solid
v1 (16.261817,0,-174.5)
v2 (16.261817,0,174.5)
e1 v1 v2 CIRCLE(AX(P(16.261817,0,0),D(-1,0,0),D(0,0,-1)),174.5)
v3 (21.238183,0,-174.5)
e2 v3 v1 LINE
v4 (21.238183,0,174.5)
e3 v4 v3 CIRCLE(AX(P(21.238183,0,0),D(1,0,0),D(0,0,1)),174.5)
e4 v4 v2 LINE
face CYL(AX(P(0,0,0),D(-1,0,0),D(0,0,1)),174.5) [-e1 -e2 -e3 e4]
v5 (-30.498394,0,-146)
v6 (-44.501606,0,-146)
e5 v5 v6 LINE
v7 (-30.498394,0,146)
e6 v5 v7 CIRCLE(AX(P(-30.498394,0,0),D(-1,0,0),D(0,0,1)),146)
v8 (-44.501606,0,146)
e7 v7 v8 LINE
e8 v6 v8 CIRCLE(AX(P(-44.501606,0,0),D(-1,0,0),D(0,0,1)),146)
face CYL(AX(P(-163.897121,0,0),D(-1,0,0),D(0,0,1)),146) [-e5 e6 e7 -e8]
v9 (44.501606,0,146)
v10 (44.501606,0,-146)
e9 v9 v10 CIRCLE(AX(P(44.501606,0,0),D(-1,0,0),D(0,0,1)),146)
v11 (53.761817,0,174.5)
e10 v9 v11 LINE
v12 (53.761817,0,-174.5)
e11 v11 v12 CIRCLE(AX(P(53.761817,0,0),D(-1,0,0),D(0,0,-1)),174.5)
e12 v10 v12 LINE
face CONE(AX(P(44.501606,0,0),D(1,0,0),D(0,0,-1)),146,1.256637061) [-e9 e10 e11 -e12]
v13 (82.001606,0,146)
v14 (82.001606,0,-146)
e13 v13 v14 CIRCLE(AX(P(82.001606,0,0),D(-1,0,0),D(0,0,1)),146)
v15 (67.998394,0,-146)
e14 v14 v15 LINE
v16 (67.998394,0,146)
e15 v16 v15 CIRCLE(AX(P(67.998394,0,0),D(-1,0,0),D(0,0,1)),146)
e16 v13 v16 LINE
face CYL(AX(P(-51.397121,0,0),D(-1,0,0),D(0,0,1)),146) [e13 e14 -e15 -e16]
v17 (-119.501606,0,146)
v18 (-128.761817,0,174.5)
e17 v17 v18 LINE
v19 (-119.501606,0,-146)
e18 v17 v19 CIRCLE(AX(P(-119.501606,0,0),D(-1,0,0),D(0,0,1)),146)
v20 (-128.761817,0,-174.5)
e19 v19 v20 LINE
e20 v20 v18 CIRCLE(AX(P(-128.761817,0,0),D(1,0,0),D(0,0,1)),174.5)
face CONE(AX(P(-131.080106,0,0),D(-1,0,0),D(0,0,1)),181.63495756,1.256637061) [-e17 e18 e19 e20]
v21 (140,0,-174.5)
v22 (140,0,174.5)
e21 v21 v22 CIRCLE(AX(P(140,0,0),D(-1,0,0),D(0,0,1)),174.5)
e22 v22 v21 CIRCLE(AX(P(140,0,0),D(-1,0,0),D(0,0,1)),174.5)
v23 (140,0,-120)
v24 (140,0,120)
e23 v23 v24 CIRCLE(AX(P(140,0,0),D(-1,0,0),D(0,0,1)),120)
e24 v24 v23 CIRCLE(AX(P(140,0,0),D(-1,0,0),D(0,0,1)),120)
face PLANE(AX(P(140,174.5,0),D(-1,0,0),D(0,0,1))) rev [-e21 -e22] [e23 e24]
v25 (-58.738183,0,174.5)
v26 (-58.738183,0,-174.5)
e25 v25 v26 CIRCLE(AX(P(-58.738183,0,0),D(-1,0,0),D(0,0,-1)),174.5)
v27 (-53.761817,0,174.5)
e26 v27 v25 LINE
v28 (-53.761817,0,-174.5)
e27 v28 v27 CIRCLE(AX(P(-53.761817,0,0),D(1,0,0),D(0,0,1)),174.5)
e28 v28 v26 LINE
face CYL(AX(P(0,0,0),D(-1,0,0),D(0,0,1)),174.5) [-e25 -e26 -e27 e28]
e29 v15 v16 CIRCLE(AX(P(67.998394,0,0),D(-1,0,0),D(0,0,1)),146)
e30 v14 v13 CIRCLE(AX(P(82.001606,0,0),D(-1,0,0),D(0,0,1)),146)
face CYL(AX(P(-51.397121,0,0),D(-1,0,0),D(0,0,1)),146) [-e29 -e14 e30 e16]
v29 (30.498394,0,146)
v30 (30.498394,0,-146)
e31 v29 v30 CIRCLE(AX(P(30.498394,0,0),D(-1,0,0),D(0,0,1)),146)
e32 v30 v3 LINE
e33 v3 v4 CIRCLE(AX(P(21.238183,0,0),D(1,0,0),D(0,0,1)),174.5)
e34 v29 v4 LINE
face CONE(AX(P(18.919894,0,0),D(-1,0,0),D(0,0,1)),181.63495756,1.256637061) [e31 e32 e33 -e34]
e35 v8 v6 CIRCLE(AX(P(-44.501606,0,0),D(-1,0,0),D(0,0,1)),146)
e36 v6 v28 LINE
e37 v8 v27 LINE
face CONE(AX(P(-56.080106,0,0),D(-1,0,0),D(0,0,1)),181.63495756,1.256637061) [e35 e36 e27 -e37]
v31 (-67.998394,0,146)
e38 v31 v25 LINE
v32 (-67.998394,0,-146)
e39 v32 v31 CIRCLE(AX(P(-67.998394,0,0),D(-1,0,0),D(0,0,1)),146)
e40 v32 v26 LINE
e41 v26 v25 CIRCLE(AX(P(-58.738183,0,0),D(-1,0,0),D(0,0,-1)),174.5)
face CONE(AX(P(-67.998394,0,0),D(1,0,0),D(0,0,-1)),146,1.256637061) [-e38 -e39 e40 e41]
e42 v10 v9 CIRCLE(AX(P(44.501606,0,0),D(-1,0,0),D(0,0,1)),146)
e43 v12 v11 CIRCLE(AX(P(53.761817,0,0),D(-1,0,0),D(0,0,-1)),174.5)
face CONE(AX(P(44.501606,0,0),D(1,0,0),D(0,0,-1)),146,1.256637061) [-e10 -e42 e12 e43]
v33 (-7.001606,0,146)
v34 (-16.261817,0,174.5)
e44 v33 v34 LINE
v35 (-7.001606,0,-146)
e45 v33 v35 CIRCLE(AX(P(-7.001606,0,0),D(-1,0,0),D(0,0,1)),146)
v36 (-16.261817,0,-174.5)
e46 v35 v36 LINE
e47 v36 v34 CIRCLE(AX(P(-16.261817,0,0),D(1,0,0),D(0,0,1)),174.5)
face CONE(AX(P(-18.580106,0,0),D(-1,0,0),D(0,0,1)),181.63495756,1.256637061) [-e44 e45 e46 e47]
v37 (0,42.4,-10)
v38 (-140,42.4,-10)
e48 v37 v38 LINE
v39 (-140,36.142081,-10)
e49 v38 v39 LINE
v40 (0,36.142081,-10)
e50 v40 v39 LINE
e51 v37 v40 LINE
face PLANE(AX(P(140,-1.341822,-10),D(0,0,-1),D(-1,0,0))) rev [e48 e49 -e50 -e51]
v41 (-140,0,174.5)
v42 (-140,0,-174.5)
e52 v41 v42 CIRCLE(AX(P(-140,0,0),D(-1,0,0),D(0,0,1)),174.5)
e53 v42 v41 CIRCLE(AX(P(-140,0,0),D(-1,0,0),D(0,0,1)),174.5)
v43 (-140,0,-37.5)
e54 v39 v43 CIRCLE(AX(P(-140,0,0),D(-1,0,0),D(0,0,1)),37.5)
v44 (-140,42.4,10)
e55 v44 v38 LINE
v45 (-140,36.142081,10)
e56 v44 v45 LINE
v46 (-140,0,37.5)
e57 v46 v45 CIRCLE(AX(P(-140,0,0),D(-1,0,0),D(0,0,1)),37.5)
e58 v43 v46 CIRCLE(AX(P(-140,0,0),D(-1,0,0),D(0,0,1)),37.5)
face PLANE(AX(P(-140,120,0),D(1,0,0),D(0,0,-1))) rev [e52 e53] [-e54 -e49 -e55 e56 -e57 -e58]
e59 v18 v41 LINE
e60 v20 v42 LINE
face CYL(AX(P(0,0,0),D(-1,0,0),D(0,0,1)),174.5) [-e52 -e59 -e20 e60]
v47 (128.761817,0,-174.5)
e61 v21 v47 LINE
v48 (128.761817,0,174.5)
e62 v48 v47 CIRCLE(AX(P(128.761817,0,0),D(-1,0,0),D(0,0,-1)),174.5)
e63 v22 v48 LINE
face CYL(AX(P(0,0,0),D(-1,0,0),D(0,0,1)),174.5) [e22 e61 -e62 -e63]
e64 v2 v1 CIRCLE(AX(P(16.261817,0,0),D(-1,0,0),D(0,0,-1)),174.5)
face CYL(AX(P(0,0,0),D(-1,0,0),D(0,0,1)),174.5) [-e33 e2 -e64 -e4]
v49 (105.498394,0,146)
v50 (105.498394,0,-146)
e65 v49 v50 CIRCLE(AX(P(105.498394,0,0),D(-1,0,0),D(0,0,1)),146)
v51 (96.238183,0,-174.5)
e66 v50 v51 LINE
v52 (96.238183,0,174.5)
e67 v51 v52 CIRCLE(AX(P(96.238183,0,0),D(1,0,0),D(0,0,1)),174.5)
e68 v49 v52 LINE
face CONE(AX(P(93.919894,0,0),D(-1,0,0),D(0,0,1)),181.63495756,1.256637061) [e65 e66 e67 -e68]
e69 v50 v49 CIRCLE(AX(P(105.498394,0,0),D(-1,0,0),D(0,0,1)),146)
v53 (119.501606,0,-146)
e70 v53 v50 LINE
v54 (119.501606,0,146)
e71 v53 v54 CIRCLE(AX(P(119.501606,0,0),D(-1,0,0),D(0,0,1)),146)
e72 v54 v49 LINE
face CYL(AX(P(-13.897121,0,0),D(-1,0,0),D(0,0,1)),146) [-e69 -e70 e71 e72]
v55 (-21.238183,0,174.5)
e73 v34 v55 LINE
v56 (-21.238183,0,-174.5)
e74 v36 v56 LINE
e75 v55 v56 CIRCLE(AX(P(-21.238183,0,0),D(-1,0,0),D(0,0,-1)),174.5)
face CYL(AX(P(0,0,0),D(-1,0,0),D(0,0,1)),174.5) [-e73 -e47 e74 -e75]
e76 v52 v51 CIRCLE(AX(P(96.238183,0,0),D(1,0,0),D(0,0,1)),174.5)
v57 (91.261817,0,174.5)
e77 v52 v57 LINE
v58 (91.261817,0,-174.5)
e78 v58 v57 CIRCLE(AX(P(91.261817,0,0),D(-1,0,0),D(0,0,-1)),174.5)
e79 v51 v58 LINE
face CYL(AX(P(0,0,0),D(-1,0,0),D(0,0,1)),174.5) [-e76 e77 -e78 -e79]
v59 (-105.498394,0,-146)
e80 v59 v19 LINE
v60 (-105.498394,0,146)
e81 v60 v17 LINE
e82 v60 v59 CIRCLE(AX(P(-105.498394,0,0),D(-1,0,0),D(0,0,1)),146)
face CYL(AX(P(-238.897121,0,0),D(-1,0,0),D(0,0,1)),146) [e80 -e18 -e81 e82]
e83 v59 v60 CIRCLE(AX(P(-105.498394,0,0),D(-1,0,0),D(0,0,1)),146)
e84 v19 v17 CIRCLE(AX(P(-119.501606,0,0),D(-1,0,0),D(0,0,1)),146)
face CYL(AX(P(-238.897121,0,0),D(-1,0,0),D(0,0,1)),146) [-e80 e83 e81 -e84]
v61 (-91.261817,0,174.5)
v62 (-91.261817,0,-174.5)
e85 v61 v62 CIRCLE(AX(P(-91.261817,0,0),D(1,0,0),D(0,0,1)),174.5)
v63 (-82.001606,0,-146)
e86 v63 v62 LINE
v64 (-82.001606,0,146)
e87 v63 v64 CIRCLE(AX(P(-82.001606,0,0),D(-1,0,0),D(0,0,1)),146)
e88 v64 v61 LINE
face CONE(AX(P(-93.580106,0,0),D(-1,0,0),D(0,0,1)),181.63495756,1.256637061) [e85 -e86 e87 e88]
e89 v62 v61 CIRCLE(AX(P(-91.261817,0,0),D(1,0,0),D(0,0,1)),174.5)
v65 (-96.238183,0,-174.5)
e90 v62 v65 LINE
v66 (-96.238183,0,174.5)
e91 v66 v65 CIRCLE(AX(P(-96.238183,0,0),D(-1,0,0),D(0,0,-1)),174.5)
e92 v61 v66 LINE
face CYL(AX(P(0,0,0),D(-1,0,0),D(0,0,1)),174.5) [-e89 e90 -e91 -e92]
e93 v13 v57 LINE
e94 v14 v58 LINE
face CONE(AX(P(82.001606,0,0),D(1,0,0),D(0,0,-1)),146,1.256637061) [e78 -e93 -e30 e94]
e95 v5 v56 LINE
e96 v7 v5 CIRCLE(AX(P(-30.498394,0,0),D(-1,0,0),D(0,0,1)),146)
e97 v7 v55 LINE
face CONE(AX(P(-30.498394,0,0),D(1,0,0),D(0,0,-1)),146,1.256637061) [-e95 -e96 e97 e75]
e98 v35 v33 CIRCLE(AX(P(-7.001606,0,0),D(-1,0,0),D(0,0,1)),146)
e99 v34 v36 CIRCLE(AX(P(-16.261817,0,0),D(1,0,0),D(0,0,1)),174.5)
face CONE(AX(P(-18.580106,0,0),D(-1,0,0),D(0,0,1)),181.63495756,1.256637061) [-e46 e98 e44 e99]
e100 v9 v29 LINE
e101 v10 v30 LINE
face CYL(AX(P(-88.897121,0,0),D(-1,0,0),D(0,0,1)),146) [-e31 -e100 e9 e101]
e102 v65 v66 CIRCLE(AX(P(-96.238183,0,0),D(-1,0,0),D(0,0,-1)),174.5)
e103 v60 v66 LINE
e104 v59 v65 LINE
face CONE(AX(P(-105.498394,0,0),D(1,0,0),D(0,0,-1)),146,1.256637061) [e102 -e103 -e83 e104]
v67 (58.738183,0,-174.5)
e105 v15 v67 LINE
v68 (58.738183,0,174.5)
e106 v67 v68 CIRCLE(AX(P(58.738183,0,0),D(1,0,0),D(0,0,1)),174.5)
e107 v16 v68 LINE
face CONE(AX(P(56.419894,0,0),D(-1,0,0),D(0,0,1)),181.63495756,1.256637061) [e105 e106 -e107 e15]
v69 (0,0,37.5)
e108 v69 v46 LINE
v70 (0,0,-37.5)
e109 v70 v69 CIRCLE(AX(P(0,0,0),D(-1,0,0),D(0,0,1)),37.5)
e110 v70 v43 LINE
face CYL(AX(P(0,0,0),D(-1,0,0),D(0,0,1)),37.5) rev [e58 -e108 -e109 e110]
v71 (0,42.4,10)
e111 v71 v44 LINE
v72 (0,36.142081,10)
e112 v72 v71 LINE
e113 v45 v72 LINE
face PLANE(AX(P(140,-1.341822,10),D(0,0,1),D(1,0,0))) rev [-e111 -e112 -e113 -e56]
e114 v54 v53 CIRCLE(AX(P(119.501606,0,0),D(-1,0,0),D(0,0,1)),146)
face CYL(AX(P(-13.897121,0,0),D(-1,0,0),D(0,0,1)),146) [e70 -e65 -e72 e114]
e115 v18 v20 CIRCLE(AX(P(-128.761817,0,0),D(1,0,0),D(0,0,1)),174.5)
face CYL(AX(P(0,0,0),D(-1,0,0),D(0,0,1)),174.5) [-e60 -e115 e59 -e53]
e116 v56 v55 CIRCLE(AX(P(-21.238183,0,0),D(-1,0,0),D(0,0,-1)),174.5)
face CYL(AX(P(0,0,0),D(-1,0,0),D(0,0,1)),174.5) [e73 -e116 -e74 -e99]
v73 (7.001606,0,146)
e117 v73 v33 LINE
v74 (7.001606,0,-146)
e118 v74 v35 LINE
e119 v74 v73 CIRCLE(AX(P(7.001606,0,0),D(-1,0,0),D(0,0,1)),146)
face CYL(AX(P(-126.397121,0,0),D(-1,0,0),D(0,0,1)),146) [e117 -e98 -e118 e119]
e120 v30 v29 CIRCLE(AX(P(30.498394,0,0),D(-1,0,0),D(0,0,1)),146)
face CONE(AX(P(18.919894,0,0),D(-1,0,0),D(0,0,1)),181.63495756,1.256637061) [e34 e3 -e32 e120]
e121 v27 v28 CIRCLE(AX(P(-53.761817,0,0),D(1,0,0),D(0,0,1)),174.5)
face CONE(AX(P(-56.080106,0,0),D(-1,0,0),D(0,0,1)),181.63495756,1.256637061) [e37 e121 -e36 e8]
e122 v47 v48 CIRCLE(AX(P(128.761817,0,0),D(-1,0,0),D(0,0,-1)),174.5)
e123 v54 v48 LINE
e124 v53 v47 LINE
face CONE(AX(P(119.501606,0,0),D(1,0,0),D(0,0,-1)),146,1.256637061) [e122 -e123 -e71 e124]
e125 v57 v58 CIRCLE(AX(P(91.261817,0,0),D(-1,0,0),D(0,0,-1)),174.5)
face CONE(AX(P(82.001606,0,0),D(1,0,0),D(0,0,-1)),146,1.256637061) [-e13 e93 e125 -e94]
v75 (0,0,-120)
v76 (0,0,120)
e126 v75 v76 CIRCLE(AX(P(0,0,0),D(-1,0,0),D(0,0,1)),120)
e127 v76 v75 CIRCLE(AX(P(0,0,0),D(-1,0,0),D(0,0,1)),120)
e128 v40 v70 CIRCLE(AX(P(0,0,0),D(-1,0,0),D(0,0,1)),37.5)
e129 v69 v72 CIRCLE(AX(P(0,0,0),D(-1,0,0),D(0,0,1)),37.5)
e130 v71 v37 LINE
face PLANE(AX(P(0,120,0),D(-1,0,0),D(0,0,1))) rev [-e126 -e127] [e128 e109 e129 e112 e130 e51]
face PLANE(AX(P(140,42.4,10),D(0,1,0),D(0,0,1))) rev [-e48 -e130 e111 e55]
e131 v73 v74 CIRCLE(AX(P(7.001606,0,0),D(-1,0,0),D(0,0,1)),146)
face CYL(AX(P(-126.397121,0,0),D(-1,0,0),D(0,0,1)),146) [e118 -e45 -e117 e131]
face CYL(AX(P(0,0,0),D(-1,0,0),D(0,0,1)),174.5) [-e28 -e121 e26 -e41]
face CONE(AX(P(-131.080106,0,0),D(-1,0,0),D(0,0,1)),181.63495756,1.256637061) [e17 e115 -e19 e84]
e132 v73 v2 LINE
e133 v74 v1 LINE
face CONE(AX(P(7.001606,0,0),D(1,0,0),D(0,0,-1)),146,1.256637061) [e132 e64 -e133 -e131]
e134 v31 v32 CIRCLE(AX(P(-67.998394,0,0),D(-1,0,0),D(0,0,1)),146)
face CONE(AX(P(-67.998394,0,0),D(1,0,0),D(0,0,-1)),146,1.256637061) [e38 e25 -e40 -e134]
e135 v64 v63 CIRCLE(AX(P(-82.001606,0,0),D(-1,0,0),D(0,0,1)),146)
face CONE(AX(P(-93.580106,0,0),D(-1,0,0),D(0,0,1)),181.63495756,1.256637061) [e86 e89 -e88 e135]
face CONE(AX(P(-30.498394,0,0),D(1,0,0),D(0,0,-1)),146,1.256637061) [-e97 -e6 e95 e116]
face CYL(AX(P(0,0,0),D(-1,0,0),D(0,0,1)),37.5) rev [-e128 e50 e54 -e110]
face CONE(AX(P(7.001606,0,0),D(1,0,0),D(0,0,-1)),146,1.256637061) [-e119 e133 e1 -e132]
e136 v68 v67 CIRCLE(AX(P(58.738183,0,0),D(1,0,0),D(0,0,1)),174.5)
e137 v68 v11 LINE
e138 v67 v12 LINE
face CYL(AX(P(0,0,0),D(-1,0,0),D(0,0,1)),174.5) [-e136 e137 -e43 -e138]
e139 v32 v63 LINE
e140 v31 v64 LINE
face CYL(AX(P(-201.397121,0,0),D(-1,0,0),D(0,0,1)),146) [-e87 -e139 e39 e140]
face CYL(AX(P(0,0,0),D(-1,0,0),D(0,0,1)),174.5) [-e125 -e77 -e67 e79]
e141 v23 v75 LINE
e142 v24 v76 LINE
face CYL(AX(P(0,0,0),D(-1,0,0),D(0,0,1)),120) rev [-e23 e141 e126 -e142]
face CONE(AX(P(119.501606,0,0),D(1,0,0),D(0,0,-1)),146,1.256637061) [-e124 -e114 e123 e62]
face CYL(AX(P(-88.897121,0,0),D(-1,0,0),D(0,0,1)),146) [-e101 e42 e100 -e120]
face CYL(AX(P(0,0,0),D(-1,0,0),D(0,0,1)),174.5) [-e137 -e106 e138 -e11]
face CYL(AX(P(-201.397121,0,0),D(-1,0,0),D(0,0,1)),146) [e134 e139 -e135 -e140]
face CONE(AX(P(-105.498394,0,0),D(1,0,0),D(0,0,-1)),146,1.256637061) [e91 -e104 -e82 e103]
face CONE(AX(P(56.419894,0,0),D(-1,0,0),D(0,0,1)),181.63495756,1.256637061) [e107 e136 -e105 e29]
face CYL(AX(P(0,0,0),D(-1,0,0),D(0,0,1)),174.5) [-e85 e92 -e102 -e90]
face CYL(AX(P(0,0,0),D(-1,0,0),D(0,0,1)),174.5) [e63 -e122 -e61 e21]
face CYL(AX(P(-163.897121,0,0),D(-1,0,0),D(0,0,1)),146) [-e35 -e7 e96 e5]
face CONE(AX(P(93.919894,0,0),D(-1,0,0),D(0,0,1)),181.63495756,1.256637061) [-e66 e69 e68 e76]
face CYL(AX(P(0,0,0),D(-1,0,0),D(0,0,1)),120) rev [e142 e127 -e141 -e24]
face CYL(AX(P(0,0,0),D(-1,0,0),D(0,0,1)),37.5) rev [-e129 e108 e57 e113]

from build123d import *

# Parameters (mm, degrees)
SKETCH3_W          = 20
SKETCH3_H          = 43.741822135
CUT_EXTRUDE1_DEPTH = 374.22982196
LPATTERN1_COUNT    = 7
LPATTERN1_PITCH    = 37.5


with BuildPart() as part:
    # Sketch1 → Revolve1 (revolve)
    with BuildSketch(Plane.XY, mode=Mode.PRIVATE) as revolve1_sk:
        Polygon((0, 37.5), (-140, 37.5), (-140, 120), (-140, 174.5), (140, 174.5), (140, 120), (0, 120), align=None)
    revolve(revolve1_sk.sketch.rotate(Axis((0, 0, 0), (1, 0, 0)), 90), axis=Axis((0, 0, 0), (1, 0, 0)))

    # Sketch2 → Cut-Revolve1 (revolve, cut)
    with BuildSketch(Plane(origin=(0, 0, 0), x_dir=(1, 0, 0), z_dir=(0, 1, 0)), mode=Mode.PRIVATE) as cut_revolve1_sk:
        Polygon((-131.080105661, 181.63495756), (-119.501606075, 146), (-105.498393925, 146), (-93.919894339, 181.63495756), align=None)
    cut_revolve1 = revolve(cut_revolve1_sk.sketch.rotate(Axis((-238.897121458, 0, 0), (1, 0, 0)), 180), axis=Axis((-238.897121458, 0, 0), (1, 0, 0)), mode=Mode.SUBTRACT)

    # Sketch3 → Cut-Extrude1 (cut, through all)
    with BuildSketch(Plane.ZY.offset(140)):
        with Locations((0, 20.529088933)):
            Rectangle(SKETCH3_W, SKETCH3_H)
    extrude(amount=-CUT_EXTRUDE1_DEPTH, mode=Mode.SUBTRACT)

    # LPattern1: Cut-Revolve1 ×7
    with Locations(*[(i * LPATTERN1_PITCH, 0, 0) for i in range(1, LPATTERN1_COUNT)]):
        add(cut_revolve1, mode=Mode.SUBTRACT)


solid = part.part
